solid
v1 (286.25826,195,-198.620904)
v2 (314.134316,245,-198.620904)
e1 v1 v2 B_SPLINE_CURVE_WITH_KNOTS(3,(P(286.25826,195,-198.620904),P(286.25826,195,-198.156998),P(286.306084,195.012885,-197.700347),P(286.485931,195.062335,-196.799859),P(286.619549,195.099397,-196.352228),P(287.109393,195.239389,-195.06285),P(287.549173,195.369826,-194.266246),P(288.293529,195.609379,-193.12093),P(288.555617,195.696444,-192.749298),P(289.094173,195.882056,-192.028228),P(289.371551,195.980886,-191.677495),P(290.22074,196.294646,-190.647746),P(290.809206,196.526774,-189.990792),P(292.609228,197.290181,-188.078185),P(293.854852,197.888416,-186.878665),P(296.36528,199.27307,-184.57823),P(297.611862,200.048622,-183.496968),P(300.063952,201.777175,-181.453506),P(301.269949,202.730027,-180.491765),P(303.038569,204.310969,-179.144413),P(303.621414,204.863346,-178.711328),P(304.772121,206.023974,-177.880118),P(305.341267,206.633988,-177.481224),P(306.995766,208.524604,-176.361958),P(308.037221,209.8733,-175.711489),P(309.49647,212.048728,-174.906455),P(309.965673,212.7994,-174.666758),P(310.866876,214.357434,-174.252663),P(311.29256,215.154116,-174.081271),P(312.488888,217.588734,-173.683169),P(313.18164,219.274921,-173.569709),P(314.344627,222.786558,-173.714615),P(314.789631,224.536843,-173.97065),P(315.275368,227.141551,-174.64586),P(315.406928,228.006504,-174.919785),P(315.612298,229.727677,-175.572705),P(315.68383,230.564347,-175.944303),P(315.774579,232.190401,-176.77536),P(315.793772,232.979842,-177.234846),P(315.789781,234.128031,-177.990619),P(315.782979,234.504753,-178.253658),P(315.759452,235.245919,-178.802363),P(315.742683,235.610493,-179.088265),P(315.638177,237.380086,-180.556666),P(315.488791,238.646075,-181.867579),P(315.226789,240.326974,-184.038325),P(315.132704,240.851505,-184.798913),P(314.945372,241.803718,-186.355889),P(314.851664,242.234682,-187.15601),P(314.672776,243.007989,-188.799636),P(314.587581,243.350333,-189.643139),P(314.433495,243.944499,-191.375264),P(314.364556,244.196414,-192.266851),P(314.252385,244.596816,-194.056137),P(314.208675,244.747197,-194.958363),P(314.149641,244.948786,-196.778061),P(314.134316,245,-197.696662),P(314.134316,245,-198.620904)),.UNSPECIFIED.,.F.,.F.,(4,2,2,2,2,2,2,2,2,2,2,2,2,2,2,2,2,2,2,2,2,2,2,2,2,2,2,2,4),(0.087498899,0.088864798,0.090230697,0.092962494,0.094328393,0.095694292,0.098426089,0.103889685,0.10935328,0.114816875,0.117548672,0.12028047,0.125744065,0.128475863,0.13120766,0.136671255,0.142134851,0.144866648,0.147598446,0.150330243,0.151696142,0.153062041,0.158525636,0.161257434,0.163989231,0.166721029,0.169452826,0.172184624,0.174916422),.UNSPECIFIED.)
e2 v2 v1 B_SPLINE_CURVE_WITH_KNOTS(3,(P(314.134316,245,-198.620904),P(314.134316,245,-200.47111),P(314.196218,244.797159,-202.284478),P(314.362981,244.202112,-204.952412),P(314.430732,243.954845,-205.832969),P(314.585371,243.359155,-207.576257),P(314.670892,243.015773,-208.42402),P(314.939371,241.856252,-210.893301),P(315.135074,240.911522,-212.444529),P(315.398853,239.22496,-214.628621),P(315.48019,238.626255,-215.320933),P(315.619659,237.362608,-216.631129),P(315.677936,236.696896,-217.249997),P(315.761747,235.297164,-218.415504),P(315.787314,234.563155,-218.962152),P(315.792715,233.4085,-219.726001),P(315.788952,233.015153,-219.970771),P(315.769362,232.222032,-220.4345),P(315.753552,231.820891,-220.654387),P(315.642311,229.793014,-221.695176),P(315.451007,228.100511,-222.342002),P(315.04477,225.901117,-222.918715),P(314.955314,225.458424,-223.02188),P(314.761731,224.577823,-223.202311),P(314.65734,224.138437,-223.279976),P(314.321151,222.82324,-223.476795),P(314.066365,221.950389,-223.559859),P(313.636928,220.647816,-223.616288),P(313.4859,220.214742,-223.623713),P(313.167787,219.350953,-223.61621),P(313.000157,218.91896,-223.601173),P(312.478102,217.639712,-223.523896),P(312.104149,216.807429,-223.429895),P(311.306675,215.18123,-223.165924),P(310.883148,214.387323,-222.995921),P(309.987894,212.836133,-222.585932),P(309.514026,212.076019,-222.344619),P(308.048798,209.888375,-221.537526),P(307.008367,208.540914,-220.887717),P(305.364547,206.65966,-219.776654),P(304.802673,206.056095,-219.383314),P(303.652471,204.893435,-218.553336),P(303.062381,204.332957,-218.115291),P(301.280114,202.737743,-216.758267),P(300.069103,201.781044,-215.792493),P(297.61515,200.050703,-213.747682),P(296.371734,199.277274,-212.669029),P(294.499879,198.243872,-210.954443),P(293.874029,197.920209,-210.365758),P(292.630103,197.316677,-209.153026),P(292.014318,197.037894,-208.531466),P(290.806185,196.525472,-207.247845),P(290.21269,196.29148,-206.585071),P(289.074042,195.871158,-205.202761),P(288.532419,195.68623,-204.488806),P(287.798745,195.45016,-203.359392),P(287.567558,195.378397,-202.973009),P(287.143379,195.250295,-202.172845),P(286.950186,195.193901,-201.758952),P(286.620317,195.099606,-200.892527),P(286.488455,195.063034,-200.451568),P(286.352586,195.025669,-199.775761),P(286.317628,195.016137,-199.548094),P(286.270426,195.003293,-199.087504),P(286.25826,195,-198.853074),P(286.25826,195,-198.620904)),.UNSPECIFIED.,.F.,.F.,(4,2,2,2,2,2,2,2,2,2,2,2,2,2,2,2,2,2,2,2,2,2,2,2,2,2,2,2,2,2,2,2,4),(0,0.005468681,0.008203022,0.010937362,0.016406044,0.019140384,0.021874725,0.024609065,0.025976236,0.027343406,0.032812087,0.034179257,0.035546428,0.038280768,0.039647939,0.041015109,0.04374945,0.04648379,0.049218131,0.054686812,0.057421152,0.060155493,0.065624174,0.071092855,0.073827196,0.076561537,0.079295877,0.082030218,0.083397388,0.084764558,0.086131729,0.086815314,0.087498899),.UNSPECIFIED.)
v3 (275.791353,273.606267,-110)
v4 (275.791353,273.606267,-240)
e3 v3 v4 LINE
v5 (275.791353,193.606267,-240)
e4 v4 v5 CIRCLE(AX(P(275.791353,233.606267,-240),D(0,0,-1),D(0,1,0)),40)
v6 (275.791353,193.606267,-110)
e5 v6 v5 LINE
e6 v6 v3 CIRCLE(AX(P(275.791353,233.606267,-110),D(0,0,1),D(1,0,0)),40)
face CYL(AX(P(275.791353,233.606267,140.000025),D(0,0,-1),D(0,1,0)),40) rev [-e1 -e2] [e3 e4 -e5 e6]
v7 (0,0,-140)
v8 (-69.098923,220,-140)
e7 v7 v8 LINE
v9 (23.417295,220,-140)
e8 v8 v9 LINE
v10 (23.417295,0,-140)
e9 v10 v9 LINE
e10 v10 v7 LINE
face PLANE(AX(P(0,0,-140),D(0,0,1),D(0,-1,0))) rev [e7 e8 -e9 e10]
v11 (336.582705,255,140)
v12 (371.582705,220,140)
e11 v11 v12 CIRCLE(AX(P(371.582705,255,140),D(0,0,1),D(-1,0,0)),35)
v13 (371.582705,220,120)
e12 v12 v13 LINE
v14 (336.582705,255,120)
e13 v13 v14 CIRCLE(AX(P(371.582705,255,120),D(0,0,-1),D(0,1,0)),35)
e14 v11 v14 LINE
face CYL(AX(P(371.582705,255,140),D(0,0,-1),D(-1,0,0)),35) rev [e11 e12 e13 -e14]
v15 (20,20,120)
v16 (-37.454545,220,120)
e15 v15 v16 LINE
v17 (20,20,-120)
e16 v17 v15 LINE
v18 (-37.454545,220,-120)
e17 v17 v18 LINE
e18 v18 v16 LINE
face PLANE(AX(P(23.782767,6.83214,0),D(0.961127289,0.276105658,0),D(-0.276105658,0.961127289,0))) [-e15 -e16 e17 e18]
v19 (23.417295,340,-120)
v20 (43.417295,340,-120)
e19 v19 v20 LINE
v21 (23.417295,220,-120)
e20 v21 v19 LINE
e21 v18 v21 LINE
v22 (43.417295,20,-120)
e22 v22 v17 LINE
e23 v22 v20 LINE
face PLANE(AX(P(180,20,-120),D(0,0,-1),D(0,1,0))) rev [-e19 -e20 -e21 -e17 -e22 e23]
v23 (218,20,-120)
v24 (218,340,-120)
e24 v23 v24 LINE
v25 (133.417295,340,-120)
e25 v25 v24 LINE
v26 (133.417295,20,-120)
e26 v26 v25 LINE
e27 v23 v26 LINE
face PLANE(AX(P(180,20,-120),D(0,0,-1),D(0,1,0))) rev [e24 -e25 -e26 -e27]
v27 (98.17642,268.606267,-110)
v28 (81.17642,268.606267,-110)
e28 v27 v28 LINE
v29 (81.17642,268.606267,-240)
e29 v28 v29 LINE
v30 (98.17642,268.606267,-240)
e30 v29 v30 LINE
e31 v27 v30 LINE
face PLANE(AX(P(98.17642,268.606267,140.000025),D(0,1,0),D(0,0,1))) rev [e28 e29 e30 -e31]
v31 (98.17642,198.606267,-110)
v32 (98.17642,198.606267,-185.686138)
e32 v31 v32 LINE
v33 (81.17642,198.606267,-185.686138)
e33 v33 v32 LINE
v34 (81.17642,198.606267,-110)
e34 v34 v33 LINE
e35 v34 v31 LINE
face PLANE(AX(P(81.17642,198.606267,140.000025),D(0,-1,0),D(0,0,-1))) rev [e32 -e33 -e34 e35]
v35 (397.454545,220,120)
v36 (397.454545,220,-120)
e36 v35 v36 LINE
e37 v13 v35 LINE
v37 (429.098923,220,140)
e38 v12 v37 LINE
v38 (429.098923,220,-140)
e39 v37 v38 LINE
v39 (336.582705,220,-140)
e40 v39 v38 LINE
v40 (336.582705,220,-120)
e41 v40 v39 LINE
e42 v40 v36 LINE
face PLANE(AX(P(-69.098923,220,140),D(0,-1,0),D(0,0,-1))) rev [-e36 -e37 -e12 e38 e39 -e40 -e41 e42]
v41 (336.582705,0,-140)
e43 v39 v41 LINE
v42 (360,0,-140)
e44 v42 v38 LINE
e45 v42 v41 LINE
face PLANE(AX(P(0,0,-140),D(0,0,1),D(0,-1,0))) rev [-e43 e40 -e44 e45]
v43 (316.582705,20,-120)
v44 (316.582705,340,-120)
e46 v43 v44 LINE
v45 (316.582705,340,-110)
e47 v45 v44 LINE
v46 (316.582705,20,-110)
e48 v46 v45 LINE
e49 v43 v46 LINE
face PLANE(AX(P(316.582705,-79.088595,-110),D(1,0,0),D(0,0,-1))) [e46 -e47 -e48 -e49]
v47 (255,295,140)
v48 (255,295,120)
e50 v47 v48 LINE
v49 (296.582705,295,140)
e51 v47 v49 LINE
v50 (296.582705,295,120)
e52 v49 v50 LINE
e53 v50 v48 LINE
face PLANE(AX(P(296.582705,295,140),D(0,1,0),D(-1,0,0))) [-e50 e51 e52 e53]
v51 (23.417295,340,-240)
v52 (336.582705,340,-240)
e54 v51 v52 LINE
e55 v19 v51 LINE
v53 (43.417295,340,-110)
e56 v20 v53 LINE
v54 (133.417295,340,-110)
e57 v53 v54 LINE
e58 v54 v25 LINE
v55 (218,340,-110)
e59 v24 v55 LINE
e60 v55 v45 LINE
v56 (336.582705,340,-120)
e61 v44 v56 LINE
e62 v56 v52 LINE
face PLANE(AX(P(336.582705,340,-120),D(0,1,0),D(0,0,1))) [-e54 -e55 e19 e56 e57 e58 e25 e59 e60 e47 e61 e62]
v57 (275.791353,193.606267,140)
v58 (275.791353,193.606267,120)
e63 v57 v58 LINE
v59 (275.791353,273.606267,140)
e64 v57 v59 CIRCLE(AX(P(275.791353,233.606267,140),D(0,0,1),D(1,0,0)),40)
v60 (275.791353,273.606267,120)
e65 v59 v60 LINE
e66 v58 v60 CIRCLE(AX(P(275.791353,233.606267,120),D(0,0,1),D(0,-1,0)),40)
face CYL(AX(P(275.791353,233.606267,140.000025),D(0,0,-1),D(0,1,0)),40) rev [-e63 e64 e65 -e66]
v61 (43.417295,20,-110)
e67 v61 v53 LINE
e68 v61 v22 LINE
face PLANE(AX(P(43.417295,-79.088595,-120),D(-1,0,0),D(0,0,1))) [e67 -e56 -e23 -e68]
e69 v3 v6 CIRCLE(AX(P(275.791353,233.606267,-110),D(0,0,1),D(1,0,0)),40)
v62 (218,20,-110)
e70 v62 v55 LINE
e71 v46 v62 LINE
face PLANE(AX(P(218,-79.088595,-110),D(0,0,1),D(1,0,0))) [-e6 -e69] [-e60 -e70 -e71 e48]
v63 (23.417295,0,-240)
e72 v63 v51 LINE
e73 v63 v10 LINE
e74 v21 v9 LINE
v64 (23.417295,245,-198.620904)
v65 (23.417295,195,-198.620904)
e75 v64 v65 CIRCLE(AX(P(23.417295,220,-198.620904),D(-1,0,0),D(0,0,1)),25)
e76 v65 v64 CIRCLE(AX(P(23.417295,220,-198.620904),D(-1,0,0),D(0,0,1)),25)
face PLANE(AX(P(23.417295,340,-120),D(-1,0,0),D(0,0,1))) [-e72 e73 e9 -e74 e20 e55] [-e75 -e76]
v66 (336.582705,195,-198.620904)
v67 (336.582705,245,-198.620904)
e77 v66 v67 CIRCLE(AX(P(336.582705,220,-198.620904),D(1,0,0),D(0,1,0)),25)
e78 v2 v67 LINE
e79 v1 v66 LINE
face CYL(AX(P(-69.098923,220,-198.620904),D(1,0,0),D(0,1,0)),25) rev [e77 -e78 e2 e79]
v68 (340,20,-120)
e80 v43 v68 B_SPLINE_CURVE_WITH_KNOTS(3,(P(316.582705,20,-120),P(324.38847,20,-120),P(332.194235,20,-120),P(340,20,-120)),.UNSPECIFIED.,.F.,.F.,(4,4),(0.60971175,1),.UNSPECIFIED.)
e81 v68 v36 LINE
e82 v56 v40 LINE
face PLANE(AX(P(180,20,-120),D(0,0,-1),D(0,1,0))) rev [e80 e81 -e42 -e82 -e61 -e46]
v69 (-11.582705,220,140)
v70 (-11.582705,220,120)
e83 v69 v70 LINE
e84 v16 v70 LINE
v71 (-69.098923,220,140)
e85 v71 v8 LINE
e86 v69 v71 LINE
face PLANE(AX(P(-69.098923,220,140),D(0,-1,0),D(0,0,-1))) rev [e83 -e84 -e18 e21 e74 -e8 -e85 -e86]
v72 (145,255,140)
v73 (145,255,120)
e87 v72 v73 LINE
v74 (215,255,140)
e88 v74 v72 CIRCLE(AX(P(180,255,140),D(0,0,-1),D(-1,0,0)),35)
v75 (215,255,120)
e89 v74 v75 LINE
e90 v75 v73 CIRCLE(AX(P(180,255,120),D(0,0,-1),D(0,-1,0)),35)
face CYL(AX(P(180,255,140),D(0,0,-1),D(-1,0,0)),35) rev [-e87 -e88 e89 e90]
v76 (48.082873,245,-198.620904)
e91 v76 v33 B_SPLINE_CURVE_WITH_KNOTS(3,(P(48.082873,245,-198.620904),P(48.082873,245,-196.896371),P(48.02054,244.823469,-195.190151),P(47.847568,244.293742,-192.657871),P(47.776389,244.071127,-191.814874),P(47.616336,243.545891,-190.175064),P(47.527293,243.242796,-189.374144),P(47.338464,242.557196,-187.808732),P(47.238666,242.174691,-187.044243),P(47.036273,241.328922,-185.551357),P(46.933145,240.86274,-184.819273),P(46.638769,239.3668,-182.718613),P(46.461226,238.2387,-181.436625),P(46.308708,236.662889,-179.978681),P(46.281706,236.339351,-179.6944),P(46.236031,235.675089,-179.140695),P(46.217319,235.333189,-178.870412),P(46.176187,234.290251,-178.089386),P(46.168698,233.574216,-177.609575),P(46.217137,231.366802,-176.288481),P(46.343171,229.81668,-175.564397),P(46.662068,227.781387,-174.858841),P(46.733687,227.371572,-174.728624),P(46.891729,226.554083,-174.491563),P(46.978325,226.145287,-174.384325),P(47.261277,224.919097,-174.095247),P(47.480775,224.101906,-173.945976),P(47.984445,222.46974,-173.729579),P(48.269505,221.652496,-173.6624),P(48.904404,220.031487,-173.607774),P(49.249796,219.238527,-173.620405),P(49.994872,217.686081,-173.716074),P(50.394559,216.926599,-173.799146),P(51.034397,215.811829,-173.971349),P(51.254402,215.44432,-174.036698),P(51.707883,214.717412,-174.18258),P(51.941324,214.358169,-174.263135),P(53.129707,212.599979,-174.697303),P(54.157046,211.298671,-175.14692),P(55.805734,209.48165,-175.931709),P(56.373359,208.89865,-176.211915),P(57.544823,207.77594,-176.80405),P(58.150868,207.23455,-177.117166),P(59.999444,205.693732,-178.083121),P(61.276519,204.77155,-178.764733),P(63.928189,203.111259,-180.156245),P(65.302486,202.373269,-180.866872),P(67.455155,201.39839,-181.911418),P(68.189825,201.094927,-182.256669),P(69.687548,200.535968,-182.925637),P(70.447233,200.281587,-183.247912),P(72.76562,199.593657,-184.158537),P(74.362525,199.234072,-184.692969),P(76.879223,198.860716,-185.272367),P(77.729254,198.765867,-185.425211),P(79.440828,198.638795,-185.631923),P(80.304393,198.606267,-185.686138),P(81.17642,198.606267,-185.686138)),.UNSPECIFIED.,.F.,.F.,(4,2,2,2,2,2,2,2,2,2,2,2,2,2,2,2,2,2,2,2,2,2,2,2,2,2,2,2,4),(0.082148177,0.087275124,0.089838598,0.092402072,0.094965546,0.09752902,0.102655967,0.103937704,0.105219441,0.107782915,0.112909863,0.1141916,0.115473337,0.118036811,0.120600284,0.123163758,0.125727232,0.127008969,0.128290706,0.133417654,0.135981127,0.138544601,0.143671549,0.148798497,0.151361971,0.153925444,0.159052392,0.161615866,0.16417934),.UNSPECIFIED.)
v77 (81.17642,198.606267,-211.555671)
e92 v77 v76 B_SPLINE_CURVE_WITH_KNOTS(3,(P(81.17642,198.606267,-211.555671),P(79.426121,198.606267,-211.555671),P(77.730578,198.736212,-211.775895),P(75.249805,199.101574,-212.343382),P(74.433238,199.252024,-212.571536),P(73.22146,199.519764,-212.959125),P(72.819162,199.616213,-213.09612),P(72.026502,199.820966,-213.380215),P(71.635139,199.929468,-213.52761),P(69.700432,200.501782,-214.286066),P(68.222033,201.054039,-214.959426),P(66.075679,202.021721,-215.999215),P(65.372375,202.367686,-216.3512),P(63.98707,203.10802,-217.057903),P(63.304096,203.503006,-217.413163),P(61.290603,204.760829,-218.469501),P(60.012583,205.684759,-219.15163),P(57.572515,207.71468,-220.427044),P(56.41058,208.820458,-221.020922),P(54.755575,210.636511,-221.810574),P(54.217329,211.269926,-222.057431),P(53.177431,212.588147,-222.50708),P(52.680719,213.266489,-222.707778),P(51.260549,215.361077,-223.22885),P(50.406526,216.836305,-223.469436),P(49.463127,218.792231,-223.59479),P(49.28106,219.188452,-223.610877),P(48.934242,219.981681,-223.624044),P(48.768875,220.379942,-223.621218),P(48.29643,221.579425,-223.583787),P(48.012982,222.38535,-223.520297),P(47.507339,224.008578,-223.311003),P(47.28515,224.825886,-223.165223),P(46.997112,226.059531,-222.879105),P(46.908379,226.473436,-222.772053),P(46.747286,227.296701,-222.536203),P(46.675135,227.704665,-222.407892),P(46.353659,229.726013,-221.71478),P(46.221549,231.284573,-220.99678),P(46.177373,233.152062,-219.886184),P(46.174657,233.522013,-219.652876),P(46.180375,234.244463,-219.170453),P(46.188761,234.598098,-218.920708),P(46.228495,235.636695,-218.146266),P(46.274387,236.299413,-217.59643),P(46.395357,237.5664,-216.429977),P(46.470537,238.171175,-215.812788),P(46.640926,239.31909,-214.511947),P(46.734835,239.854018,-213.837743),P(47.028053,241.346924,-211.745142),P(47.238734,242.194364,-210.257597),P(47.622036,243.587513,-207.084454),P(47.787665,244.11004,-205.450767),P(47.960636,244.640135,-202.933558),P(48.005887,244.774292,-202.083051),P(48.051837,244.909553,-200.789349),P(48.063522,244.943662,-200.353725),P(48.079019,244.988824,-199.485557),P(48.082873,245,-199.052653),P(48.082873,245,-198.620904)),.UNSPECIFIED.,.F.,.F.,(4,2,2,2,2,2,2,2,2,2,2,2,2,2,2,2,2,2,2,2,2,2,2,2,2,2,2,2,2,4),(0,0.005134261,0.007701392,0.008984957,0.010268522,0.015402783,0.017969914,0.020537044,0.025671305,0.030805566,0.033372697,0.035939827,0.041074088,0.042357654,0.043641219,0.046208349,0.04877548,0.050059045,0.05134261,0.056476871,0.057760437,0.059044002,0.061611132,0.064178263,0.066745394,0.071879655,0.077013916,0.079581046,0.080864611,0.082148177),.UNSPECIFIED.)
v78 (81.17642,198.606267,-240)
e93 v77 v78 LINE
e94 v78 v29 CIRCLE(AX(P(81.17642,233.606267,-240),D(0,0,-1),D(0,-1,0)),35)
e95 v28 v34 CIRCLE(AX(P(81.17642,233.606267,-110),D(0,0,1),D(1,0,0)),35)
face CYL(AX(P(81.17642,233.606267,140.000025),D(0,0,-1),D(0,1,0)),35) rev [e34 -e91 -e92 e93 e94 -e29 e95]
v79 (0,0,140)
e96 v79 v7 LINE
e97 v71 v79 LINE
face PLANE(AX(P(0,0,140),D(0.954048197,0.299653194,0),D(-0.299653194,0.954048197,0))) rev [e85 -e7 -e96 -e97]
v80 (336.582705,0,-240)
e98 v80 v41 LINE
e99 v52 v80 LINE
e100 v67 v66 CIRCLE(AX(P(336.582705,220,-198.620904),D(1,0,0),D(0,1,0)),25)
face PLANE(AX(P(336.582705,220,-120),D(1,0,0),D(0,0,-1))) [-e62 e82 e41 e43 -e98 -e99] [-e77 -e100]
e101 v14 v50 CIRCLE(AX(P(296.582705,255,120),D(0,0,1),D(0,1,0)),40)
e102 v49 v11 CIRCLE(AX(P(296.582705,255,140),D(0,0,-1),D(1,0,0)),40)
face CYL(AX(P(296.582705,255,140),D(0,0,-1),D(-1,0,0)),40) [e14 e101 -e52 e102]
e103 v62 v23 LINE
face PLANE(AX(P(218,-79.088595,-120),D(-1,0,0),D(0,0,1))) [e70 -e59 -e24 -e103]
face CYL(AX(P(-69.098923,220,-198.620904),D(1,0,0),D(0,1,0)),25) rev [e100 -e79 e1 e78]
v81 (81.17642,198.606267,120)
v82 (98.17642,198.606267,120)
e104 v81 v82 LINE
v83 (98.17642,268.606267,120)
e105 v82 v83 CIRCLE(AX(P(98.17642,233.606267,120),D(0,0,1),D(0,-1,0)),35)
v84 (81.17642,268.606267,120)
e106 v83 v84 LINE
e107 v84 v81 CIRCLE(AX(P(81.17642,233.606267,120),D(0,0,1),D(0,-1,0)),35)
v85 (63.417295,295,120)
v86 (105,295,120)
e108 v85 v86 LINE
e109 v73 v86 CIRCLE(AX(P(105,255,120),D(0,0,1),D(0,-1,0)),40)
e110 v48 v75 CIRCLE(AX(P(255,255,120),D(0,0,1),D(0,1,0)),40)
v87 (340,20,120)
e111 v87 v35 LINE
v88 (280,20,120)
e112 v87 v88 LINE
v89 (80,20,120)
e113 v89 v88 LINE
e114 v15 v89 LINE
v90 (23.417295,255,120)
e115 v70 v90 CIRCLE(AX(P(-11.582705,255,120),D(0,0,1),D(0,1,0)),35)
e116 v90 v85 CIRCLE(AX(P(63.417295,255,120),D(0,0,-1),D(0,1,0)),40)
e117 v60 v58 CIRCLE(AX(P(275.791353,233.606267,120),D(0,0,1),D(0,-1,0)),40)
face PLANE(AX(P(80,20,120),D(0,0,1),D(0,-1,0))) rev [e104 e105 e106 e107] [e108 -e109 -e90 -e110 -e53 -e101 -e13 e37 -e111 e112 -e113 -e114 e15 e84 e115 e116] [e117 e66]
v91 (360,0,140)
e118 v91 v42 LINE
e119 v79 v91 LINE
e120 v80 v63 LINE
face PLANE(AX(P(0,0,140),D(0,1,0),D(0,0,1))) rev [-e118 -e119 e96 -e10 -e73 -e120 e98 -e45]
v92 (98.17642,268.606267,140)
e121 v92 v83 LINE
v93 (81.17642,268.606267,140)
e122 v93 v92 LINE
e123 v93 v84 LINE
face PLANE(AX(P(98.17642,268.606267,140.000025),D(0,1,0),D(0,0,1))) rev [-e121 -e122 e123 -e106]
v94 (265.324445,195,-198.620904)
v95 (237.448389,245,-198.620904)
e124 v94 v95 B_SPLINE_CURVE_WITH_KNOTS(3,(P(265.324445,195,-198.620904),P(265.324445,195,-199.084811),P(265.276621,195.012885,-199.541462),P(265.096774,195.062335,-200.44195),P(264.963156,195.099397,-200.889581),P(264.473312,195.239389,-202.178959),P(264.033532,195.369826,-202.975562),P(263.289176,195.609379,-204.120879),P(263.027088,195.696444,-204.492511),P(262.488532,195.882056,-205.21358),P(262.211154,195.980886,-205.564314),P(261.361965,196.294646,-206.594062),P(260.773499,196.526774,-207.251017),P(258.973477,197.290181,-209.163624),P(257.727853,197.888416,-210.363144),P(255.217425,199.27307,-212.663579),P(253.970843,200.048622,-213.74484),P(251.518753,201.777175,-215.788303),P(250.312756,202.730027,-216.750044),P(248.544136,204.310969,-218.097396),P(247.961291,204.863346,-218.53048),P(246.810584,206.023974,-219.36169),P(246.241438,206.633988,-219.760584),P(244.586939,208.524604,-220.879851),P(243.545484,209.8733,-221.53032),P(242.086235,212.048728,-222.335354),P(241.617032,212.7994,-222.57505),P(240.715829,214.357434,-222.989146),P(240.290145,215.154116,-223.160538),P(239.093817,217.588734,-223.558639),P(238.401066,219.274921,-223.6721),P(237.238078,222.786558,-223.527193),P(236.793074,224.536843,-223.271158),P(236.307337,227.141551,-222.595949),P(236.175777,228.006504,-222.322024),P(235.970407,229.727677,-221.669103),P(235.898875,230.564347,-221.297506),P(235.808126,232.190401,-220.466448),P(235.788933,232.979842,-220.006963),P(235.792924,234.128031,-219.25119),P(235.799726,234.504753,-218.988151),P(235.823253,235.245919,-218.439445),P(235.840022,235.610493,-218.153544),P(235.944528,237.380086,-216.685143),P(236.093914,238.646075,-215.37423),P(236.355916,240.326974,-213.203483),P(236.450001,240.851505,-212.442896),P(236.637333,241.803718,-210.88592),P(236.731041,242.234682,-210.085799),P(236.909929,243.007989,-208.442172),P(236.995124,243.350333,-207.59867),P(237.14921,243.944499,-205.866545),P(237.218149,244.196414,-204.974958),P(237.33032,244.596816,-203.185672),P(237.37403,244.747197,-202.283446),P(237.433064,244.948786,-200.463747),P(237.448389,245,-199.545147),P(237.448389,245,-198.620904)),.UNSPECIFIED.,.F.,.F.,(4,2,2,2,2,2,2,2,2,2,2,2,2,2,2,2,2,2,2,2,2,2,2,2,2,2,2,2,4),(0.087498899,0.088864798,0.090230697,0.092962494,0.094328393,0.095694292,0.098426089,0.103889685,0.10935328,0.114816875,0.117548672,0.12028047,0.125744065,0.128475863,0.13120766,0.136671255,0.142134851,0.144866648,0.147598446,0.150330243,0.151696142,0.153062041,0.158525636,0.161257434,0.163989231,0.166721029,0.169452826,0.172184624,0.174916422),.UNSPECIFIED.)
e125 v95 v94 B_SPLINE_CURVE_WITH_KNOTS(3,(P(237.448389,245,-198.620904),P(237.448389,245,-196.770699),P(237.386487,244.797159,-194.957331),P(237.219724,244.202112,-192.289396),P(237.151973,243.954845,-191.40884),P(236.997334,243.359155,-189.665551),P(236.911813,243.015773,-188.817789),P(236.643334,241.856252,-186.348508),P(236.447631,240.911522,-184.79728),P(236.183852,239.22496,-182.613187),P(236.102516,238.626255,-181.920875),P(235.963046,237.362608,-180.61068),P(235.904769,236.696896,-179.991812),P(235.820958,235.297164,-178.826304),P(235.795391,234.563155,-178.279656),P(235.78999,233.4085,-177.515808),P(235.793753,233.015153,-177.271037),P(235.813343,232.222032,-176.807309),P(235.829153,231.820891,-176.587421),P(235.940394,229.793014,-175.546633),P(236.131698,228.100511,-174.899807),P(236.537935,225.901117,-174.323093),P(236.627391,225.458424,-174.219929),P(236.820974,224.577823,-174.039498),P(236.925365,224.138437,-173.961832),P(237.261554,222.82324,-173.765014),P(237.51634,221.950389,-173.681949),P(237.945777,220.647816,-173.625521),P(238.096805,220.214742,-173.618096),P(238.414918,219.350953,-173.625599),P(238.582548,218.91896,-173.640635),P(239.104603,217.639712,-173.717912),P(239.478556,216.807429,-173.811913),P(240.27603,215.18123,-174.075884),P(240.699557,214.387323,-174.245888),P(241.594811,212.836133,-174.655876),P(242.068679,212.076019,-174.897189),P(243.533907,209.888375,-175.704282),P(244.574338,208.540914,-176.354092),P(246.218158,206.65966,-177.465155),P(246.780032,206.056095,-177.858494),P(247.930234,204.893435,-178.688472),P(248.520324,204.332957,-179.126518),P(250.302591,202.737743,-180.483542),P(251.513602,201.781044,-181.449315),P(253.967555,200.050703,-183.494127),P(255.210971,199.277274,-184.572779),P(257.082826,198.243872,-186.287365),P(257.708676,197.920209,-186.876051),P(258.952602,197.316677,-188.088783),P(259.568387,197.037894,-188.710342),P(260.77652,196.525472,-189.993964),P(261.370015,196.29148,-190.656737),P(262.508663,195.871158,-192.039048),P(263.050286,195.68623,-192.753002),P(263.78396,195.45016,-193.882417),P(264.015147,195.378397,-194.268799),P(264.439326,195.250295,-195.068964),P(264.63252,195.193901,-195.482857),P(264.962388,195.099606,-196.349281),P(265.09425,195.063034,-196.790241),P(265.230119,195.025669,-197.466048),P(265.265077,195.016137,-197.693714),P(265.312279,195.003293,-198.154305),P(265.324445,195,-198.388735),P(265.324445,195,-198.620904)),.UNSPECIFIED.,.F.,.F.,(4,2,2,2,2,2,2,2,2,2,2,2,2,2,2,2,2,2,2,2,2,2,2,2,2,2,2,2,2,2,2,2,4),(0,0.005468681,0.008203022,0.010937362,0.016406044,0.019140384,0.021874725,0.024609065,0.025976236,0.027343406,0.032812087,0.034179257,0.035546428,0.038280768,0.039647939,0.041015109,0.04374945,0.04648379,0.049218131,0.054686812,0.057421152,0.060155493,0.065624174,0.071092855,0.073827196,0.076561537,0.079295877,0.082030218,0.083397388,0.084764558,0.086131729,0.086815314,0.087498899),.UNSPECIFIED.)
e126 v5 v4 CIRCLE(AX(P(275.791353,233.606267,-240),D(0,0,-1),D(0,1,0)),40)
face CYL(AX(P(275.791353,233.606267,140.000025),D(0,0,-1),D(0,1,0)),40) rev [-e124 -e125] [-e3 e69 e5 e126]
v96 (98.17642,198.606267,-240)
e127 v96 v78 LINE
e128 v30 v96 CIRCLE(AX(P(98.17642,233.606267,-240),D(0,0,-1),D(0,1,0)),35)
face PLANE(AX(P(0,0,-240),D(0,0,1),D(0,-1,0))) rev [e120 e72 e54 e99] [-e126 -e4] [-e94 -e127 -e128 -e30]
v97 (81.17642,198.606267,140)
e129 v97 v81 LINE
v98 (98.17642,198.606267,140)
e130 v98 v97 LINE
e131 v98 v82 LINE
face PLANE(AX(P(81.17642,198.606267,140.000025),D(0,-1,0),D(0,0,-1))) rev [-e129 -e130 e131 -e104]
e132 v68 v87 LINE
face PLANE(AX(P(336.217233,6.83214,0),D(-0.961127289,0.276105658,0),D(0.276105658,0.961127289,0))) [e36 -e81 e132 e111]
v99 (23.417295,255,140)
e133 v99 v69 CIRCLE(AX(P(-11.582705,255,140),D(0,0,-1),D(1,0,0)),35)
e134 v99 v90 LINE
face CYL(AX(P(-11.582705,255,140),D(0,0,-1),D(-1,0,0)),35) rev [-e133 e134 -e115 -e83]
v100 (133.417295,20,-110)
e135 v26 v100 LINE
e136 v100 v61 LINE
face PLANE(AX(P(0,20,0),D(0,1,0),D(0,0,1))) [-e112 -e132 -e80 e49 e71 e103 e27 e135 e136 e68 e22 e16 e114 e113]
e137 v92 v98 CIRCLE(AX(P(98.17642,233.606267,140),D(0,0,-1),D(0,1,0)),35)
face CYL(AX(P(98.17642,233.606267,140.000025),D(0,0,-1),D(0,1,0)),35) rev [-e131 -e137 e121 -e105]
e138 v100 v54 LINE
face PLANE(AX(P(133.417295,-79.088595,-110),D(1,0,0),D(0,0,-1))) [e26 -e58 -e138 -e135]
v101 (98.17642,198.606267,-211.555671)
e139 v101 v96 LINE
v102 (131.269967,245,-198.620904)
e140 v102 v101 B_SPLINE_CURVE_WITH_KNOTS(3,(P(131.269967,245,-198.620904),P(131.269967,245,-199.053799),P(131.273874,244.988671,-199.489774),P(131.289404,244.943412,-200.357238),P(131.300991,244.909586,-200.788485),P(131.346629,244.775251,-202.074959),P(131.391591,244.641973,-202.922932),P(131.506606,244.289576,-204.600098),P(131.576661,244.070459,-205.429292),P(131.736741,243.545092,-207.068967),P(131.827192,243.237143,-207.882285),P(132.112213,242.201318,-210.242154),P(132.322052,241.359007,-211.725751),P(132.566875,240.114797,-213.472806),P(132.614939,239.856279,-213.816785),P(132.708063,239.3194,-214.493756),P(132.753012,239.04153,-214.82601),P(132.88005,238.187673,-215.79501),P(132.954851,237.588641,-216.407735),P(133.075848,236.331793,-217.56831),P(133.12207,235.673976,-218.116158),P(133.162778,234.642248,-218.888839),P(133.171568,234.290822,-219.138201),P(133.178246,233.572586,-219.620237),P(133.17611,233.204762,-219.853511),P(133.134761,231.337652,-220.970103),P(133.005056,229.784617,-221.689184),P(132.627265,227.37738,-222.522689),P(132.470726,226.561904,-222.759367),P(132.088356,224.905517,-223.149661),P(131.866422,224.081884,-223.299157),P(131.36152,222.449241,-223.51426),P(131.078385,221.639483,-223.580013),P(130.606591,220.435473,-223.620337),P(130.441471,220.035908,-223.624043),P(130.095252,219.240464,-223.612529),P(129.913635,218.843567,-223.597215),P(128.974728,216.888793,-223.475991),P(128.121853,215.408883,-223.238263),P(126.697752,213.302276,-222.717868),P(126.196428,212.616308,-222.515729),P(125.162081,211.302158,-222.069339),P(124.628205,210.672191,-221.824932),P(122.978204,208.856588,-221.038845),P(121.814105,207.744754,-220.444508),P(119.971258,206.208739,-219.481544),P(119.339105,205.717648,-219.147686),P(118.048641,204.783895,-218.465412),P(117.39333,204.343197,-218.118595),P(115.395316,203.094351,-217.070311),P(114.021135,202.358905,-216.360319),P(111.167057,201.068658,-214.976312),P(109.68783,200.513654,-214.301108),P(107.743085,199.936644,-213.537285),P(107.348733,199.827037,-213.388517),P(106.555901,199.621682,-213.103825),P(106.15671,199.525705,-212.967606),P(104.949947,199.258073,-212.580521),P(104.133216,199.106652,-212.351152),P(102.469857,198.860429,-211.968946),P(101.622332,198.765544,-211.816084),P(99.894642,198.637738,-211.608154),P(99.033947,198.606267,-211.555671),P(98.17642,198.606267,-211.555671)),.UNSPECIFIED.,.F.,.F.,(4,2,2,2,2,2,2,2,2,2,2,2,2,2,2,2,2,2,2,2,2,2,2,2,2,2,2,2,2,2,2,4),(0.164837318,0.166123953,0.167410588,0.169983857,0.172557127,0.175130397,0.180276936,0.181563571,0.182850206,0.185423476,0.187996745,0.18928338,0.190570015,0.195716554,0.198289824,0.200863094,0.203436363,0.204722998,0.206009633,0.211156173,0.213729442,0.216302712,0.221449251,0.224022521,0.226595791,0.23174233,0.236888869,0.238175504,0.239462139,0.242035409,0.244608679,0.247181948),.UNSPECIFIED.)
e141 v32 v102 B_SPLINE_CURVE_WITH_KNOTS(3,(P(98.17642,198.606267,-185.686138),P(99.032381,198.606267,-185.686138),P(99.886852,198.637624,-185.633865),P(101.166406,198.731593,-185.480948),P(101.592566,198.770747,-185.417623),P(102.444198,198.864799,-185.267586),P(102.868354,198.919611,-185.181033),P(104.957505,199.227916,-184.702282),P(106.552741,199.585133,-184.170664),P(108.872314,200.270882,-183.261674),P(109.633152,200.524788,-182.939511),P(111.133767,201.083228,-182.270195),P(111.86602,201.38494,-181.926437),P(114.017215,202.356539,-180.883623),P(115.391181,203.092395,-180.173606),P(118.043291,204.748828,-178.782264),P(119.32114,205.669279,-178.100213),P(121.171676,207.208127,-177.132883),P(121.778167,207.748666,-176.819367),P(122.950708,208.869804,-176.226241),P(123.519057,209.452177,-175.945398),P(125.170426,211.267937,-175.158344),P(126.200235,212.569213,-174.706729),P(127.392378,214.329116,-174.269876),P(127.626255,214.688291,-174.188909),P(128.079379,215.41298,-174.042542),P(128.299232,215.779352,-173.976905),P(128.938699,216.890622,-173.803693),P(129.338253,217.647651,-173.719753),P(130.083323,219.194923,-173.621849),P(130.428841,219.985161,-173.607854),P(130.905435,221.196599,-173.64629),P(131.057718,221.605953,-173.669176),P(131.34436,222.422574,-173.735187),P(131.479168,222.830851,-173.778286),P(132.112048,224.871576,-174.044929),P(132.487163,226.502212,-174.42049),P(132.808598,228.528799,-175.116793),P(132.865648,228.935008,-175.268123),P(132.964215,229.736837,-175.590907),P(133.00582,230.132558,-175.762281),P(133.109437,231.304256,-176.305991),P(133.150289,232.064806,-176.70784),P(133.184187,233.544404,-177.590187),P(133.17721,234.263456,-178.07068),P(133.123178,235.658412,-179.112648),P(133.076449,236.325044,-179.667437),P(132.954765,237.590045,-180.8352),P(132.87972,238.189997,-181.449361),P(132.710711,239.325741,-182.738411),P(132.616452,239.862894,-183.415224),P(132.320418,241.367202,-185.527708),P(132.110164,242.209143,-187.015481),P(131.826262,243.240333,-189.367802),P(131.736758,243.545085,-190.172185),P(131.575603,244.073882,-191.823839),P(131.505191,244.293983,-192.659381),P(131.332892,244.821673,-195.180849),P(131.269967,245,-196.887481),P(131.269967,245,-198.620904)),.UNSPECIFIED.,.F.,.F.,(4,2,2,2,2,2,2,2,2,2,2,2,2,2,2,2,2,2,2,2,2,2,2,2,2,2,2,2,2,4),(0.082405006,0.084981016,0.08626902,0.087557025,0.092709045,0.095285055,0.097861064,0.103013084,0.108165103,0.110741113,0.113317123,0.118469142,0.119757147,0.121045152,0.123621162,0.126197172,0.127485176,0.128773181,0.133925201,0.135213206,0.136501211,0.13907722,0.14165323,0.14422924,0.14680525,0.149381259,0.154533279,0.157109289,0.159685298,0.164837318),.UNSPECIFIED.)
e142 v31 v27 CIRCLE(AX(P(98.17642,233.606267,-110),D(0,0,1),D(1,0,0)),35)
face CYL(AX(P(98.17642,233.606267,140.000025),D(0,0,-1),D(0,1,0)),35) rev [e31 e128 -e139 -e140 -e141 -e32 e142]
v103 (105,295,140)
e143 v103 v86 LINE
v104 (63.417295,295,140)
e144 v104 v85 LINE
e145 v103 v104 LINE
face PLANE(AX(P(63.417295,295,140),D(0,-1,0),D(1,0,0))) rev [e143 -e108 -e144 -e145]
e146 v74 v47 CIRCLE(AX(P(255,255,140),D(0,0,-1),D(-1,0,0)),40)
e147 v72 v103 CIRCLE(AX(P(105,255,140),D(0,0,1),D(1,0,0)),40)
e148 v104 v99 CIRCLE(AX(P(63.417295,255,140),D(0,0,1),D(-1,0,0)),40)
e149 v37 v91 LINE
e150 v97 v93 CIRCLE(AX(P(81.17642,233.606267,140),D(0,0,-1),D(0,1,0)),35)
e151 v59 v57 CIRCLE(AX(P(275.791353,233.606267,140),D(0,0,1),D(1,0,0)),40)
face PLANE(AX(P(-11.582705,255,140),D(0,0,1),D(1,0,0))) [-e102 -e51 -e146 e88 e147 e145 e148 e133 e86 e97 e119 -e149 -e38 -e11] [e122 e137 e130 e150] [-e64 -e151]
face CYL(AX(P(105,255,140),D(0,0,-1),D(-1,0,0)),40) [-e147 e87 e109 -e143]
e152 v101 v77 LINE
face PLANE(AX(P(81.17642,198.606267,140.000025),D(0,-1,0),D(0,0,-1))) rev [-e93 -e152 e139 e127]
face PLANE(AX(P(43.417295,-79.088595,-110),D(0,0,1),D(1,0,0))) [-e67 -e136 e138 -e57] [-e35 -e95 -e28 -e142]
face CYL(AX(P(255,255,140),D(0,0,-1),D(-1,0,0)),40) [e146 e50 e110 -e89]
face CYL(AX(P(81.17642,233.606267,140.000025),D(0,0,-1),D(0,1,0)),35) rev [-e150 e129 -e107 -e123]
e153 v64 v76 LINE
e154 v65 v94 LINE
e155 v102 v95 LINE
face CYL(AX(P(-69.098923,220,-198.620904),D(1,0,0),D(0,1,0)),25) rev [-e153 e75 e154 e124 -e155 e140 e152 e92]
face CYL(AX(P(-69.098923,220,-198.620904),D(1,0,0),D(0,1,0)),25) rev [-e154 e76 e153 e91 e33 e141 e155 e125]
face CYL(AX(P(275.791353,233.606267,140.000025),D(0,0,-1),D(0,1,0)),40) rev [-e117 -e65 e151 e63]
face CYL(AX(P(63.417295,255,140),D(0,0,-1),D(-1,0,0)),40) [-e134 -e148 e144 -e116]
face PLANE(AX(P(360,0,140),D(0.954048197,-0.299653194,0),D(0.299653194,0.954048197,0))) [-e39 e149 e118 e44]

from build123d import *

# Parameters (mm, degrees)
EXTRUDE_2_DEPTH          = 140
EXTRUDE_3_DEPTH          = 140
SKETCH_8_W               = 100
SKETCH_8_H               = 240
CUT_EXTRUDE_1_DEPTH      = 275
EXTRUDE_4_DEPTH          = 100
EXTRUDE_4_DEPTH_BACK     = 20
SKETCH_12_W              = 313.16541006
SKETCH_12_H              = 120
SKETCH_13_W              = 313.16541006
SKETCH_13_H              = 220
EXTRUDE_5_DEPTH          = 100
SKETCH_14_R              = 25
CUT_EXTRUDE_2_DEPTH      = 582.186358517
SKETCH_15_W              = 90
SKETCH_15_H              = 10
SKETCH_15_W_2            = 98.58270503
EXTRUDE_6_DEPTH          = 320
CUT_EXTRUDE_3_DEPTH      = 615.919414052
CUT_EXTRUDE_3_DEPTH_BACK = 615.919414052
SKETCH_16_R              = 40


with BuildPart() as part:
    # 草图1 → 凸台-拉伸2 (new body)
    with BuildSketch(Plane.XY):
        with BuildLine():
            Line((0, 0), (180, 0))
            Line((180, 0), (180, 220))
            ThreePointArc((180, 220), (155.251262658, 230.251262658), (145, 255))
            ThreePointArc((145, 255), (133.284271247, 283.284271247), (105, 295))
            Line((105, 295), (63.41729497, 295))
            ThreePointArc((63.41729497, 295), (35.133023723, 283.284271247), (23.41729497, 255))
            ThreePointArc((23.41729497, 255), (13.166032312, 230.251262658), (-11.58270503, 220))
            Line((-11.58270503, 220), (-69.098922823, 220))
            Line((-69.098922823, 220), (0, 0))
        make_face()
    extrude_2 = extrude(amount=EXTRUDE_2_DEPTH)

    # 草图5 → 凸台-拉伸3 (add)
    with BuildSketch(Plane(origin=(0, 0, 0), x_dir=(-1, 0, 0), z_dir=(0, 0, -1))):
        Polygon((-180, 220), (69.098922823, 220), (0, 0), (-180, 0), align=None)
    extrude_3 = extrude(amount=EXTRUDE_3_DEPTH)

    # 草图8 → 切除-拉伸1 (cut)
    with BuildSketch(Plane(origin=(0, 295, 0), x_dir=(1, 0, 0), z_dir=(0, 1, 0))):
        with Locations((130, 0)):
            Rectangle(SKETCH_8_W, SKETCH_8_H)
    cut_extrude_1 = extrude(amount=-CUT_EXTRUDE_1_DEPTH, mode=Mode.SUBTRACT)

    # 草图10 → 切除-放样4 section 0
    with BuildSketch(Plane(origin=(0, 20, 0), x_dir=(1, 0, 0), z_dir=(0, 1, 0))):
        with BuildLine():
            Line((80, 120), (20, 120))
            Line((20, 120), (20, -120))
            Line((20, -120), (80, -120))
            Line((80, -120), (80, 120))
        make_face()
    # 草图11 → 切除-放样4 section 1
    with BuildSketch(Plane(origin=(0, 295, 0), x_dir=(1, 0, 0), z_dir=(0, 1, 0))):
        with BuildLine():
            Line((80, 120), (80, -120))
            Line((80, -120), (-59, -120))
            Line((-59, -120), (-59, 120))
            Line((-59, 120), (80, 120))
        make_face()
    loft_4 = loft(mode=Mode.SUBTRACT)

    # 镜向1: 凸台-拉伸2, 凸台-拉伸3, 切除-拉伸1, 切除-放样4 across plane
    add(extrude_2.mirror(Plane(origin=(180, 0, 140), x_dir=(0, 0, 1), z_dir=(-1, 0, 0))))
    add(extrude_3.mirror(Plane(origin=(180, 0, 140), x_dir=(0, 0, 1), z_dir=(-1, 0, 0))))
    add(cut_extrude_1.mirror(Plane(origin=(180, 0, 140), x_dir=(0, 0, 1), z_dir=(-1, 0, 0))), mode=Mode.SUBTRACT)
    add(loft_4.mirror(Plane(origin=(180, 0, 140), x_dir=(0, 0, 1), z_dir=(-1, 0, 0))), mode=Mode.SUBTRACT)

    # 草图12 → 凸台-拉伸4 (add, two sides: drawn at the far end of the back side and taken through both)
    with BuildSketch(Plane(origin=(0, 0, -140), x_dir=(-1, 0, 0), z_dir=(0, 0, -1)).offset(-EXTRUDE_4_DEPTH_BACK)):
        with Locations((-180, 280)):
            Rectangle(SKETCH_12_W, SKETCH_12_H)
    extrude(amount=EXTRUDE_4_DEPTH + EXTRUDE_4_DEPTH_BACK)

    # 草图13 → 凸台-拉伸5 (add)
    with BuildSketch(Plane(origin=(0, 0, -140), x_dir=(-1, 0, 0), z_dir=(0, 0, -1))):
        with Locations((-180, 110)):
            Rectangle(SKETCH_13_W, SKETCH_13_H)
    extrude(amount=EXTRUDE_5_DEPTH)

    # 草图14 → 切除-拉伸2 (cut, through all)
    with BuildSketch(Plane(origin=(336.58270503, 0, 0), x_dir=(0, 0, -1), z_dir=(1, 0, 0))):
        with Locations(Location((198.620904307, 220, 0), (0, 0, 90))):
            Circle(SKETCH_14_R)
    extrude(amount=-CUT_EXTRUDE_2_DEPTH, mode=Mode.SUBTRACT)

    # 草图15 → 凸台-拉伸6 (add)
    with BuildSketch(Plane(origin=(0, 340, 0), x_dir=(1, 0, 0), z_dir=(0, 1, 0))):
        with Locations((88.41729497, 115)):
            Rectangle(SKETCH_15_W, SKETCH_15_H)
        with Locations((267.291352515, 115)):
            Rectangle(SKETCH_15_W_2, SKETCH_15_H)
    extrude(amount=-EXTRUDE_6_DEPTH)

    # 草图16 → 切除-拉伸3 (cut, two sides: drawn at the far end of the back side and taken through both)
    with BuildSketch(Plane(origin=(0, 0, -140), x_dir=(-1, 0, 0), z_dir=(0, 0, -1)).offset(-CUT_EXTRUDE_3_DEPTH_BACK)):
        with Locations(Location((-275.791352515, 233.606267036, 0), (0, 0, 90))):
            Circle(SKETCH_16_R)
        with BuildLine():
            Line((-98.176420136, 268.606267036), (-81.17642014, 268.606267036))
            ThreePointArc((-81.17642014, 268.606267036), (-46.17642014, 233.606267036), (-81.17642014, 198.606267036))
            Line((-81.17642014, 198.606267036), (-98.176420136, 198.606267036))
            ThreePointArc((-98.176420136, 198.606267036), (-133.176420136, 233.606267036), (-98.176420136, 268.606267036))
        make_face()
    extrude(amount=CUT_EXTRUDE_3_DEPTH + CUT_EXTRUDE_3_DEPTH_BACK, mode=Mode.SUBTRACT)


solid = part.part
